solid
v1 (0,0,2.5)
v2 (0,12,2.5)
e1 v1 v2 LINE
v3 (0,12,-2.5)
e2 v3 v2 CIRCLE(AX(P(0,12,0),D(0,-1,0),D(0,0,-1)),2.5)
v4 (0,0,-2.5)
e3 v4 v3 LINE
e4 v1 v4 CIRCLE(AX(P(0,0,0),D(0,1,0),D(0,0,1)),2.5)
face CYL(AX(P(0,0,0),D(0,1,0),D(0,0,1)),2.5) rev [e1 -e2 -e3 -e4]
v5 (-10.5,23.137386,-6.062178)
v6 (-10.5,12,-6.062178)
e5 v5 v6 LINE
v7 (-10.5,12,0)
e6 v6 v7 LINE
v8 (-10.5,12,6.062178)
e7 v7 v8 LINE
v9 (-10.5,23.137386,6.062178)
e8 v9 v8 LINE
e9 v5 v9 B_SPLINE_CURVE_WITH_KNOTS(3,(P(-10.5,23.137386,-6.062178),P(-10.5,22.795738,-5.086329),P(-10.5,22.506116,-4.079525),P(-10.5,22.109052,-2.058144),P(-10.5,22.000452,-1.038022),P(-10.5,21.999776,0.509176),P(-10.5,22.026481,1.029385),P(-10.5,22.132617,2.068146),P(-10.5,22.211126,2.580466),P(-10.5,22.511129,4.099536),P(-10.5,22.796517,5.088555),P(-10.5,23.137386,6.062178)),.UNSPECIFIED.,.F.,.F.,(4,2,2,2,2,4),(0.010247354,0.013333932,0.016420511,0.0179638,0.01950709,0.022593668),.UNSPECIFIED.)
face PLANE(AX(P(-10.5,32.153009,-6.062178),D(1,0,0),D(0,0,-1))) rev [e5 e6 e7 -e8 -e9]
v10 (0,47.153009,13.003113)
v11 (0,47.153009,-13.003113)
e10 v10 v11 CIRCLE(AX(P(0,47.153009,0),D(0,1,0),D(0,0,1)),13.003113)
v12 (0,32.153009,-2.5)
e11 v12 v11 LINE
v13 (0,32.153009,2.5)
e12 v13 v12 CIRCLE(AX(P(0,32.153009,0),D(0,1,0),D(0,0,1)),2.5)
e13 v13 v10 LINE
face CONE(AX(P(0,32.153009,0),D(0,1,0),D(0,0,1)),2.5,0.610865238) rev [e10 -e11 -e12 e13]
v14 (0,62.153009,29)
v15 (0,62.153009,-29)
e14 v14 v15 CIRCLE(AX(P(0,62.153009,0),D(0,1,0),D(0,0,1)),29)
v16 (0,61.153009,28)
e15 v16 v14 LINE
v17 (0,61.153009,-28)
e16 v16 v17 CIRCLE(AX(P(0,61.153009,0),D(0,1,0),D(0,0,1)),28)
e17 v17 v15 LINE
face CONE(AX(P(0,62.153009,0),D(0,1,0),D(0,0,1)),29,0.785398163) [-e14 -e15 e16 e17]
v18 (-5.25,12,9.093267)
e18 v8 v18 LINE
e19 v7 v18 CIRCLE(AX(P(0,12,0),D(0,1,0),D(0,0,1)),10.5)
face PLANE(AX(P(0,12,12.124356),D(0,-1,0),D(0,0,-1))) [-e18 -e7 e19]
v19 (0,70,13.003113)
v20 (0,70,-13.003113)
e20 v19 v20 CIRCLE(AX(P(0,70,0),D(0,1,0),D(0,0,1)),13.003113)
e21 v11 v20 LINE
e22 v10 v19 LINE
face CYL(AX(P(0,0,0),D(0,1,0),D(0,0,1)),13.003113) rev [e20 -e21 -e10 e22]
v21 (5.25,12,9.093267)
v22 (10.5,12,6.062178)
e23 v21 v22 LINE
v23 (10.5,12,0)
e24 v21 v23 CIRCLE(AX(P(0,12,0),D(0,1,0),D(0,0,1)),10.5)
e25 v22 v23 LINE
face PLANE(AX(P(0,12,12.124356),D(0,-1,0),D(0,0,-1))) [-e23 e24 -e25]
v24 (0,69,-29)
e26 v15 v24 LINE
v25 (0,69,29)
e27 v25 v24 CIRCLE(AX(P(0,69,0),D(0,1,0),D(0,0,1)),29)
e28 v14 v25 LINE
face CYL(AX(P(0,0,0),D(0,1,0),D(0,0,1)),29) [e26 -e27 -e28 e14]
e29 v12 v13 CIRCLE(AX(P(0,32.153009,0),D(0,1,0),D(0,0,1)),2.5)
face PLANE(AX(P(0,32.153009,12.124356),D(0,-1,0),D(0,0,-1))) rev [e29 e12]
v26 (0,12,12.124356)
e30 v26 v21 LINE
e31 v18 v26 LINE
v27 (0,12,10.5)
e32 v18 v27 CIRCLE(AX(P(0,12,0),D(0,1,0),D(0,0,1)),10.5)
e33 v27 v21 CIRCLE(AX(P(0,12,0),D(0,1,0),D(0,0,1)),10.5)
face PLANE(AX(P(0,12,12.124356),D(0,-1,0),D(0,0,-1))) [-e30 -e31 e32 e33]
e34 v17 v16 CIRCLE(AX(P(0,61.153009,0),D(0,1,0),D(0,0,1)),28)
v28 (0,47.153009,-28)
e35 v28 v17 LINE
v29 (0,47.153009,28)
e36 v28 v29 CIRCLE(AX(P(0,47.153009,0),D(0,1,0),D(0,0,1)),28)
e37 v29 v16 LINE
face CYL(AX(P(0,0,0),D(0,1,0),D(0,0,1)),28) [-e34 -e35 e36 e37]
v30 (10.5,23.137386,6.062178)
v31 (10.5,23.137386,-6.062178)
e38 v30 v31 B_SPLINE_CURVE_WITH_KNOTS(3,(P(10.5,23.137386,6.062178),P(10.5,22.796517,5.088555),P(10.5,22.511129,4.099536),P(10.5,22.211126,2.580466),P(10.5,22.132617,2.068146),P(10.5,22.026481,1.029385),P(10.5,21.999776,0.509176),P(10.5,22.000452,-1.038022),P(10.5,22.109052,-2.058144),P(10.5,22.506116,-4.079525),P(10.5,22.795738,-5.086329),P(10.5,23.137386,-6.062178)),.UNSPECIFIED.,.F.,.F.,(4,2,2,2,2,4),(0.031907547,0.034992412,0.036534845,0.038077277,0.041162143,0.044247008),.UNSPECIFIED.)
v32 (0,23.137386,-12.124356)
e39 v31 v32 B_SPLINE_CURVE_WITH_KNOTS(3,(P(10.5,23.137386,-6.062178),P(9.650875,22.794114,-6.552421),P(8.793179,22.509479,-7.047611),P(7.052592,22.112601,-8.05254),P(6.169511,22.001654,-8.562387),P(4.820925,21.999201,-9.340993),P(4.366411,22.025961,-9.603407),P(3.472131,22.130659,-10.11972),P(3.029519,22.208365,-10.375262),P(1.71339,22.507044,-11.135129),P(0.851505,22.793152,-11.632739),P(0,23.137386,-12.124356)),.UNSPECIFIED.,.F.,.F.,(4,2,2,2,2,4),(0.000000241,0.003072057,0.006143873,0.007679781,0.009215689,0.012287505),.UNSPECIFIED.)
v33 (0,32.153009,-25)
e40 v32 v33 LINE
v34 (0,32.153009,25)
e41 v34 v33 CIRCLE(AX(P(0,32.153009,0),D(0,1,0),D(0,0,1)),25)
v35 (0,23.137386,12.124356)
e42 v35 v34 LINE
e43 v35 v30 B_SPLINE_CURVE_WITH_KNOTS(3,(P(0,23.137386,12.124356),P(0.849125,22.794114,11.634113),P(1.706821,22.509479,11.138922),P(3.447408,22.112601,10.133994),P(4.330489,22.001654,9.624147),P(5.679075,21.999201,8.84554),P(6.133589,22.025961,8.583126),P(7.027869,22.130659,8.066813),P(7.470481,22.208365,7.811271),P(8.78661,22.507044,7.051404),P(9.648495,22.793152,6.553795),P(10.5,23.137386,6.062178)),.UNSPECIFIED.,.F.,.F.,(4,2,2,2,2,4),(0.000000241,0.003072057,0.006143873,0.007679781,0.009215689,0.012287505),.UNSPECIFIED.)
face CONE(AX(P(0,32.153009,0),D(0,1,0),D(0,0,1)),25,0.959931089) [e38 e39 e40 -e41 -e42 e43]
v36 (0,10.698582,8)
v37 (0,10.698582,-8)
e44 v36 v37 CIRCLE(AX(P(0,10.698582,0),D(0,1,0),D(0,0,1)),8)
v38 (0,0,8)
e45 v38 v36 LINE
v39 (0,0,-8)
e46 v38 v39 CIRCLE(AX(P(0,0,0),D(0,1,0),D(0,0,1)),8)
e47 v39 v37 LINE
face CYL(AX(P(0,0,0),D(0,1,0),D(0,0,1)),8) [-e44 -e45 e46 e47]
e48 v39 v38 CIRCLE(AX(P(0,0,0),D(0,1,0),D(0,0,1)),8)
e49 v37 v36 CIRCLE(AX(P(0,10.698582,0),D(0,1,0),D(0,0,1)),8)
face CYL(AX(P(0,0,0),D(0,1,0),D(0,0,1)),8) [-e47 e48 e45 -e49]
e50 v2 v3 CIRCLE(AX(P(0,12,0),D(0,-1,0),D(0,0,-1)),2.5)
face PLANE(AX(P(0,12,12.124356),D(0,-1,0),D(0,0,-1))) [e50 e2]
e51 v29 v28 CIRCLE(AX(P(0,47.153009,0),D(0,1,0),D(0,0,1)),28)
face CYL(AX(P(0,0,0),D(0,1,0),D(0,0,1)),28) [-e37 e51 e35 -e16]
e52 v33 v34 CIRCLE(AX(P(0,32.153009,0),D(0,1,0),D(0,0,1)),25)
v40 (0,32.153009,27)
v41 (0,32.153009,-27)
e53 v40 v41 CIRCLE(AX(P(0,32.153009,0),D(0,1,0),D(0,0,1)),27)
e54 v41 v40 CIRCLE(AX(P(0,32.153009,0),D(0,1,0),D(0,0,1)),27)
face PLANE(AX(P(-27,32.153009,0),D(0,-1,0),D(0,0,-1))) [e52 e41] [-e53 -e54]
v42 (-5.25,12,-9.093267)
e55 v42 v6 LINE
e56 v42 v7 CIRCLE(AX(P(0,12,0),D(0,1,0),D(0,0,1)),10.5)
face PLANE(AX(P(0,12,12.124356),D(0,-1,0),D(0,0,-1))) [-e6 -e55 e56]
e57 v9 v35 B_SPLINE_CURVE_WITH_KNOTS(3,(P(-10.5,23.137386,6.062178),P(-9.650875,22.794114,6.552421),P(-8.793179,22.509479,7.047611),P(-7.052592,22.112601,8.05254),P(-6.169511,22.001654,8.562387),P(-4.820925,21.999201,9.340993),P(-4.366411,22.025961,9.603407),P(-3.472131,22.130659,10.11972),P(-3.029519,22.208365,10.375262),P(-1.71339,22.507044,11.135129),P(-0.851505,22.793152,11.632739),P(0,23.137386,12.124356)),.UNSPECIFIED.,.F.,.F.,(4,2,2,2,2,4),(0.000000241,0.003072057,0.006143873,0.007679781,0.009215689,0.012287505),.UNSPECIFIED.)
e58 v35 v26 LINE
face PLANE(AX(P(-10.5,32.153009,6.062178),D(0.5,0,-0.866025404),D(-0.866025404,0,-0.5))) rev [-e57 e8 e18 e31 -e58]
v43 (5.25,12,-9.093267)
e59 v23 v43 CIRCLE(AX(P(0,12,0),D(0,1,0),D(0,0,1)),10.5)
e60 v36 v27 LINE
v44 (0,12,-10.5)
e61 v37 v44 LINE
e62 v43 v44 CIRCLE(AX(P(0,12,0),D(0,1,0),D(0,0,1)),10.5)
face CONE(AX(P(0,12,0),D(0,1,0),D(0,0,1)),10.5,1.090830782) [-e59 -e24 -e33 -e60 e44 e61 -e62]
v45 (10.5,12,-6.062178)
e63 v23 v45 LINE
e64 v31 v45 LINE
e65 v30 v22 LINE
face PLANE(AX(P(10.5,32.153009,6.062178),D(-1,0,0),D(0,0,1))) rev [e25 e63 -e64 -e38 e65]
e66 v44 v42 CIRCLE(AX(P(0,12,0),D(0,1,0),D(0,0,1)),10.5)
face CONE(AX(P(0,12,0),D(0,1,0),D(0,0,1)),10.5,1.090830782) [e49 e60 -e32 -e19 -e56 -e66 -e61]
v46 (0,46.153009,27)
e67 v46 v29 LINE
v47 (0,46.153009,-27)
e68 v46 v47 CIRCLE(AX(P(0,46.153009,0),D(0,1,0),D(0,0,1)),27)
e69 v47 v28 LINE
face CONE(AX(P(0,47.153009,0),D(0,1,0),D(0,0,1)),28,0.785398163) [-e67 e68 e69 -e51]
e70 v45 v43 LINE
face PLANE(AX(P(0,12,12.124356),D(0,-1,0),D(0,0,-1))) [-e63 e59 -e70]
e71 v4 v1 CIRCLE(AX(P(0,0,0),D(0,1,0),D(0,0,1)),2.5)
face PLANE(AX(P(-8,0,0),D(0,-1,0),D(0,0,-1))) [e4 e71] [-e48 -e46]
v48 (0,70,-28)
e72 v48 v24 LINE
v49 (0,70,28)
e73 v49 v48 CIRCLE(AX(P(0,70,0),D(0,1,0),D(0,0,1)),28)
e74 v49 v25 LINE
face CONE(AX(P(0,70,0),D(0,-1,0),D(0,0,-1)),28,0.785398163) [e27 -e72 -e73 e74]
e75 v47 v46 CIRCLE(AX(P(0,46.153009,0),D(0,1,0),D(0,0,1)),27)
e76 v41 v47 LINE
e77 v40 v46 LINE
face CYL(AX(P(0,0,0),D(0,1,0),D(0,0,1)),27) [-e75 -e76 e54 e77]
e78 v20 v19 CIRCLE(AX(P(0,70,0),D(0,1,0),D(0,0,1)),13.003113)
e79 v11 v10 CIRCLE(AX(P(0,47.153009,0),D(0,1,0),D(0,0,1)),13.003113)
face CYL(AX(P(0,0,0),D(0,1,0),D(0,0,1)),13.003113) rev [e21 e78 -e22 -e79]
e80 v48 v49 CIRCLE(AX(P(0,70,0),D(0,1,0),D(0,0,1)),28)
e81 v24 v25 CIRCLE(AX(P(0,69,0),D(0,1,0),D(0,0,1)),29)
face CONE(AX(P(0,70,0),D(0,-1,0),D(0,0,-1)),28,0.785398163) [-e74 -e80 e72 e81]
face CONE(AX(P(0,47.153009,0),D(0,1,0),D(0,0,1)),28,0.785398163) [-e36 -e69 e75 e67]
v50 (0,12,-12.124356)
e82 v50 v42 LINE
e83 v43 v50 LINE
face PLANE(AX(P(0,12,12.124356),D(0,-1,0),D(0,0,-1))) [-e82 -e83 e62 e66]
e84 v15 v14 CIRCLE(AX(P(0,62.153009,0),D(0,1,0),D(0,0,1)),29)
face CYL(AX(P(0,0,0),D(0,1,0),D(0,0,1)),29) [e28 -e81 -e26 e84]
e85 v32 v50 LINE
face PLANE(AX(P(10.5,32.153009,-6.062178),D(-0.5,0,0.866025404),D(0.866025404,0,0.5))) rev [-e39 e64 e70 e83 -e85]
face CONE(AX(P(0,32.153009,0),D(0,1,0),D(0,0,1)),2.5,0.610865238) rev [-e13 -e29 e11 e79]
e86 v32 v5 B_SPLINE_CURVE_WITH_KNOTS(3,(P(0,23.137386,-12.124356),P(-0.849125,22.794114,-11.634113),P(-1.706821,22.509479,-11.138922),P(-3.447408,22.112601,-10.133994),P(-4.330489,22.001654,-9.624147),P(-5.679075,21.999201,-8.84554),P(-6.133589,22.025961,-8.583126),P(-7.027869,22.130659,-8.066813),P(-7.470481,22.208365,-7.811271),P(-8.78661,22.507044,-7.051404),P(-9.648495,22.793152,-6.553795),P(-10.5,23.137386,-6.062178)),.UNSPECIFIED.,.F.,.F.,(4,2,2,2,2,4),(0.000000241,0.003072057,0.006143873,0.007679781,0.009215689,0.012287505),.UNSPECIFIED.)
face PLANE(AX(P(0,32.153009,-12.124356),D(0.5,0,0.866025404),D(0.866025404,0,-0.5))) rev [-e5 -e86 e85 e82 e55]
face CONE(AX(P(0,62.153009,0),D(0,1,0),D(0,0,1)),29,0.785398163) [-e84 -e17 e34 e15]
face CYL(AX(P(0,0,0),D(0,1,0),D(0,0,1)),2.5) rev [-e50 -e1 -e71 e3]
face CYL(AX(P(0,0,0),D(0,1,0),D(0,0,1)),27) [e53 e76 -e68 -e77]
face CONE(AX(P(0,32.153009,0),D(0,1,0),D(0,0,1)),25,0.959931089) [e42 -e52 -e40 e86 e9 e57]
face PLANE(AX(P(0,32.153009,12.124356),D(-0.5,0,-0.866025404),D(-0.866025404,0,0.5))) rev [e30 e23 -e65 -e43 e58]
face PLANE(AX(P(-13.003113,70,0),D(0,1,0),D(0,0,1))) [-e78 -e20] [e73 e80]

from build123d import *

# Parameters (mm, degrees)
EXTRUDE1_DEPTH = 20.153009


with BuildPart() as part:
    # Sketch1 → Revolve1 (revolve)
    with BuildSketch(Plane.XY, mode=Mode.PRIVATE) as revolve1_sk:
        Polygon((-28, 70), (-29, 69), (-29, 62.153009304), (-28, 61.153009304), (-28, 47.153009304), (-27, 46.153009304), (-27, 32.153009304), (-25, 32.153009304), (-10.5, 22), (-10.5, 12), (-8, 10.698582374), (-8, 0), (-2.5, 0), (-2.5, 32.153009304), (-13.003113073, 47.153009304), (-13.003113073, 70), align=None)
    revolve(revolve1_sk.sketch.rotate(Axis((0, 0, 0), (0, -1, 0)), 270), axis=Axis((0, 0, 0), (0, -1, 0)))

    # Sketch2 → Extrude1 (add)
    with BuildSketch(Plane(origin=(0, 12, 0), x_dir=(-1, 0, 0), z_dir=(0, 1, 0))):
        Polygon((-10.5, 6.062177826), (-10.5, -6.062177826), (0, -12.124355653), (10.5, -6.062177826), (10.5, 6.062177826), (0, 12.124355653), align=None)
    extrude(amount=EXTRUDE1_DEPTH)


solid = part.part
